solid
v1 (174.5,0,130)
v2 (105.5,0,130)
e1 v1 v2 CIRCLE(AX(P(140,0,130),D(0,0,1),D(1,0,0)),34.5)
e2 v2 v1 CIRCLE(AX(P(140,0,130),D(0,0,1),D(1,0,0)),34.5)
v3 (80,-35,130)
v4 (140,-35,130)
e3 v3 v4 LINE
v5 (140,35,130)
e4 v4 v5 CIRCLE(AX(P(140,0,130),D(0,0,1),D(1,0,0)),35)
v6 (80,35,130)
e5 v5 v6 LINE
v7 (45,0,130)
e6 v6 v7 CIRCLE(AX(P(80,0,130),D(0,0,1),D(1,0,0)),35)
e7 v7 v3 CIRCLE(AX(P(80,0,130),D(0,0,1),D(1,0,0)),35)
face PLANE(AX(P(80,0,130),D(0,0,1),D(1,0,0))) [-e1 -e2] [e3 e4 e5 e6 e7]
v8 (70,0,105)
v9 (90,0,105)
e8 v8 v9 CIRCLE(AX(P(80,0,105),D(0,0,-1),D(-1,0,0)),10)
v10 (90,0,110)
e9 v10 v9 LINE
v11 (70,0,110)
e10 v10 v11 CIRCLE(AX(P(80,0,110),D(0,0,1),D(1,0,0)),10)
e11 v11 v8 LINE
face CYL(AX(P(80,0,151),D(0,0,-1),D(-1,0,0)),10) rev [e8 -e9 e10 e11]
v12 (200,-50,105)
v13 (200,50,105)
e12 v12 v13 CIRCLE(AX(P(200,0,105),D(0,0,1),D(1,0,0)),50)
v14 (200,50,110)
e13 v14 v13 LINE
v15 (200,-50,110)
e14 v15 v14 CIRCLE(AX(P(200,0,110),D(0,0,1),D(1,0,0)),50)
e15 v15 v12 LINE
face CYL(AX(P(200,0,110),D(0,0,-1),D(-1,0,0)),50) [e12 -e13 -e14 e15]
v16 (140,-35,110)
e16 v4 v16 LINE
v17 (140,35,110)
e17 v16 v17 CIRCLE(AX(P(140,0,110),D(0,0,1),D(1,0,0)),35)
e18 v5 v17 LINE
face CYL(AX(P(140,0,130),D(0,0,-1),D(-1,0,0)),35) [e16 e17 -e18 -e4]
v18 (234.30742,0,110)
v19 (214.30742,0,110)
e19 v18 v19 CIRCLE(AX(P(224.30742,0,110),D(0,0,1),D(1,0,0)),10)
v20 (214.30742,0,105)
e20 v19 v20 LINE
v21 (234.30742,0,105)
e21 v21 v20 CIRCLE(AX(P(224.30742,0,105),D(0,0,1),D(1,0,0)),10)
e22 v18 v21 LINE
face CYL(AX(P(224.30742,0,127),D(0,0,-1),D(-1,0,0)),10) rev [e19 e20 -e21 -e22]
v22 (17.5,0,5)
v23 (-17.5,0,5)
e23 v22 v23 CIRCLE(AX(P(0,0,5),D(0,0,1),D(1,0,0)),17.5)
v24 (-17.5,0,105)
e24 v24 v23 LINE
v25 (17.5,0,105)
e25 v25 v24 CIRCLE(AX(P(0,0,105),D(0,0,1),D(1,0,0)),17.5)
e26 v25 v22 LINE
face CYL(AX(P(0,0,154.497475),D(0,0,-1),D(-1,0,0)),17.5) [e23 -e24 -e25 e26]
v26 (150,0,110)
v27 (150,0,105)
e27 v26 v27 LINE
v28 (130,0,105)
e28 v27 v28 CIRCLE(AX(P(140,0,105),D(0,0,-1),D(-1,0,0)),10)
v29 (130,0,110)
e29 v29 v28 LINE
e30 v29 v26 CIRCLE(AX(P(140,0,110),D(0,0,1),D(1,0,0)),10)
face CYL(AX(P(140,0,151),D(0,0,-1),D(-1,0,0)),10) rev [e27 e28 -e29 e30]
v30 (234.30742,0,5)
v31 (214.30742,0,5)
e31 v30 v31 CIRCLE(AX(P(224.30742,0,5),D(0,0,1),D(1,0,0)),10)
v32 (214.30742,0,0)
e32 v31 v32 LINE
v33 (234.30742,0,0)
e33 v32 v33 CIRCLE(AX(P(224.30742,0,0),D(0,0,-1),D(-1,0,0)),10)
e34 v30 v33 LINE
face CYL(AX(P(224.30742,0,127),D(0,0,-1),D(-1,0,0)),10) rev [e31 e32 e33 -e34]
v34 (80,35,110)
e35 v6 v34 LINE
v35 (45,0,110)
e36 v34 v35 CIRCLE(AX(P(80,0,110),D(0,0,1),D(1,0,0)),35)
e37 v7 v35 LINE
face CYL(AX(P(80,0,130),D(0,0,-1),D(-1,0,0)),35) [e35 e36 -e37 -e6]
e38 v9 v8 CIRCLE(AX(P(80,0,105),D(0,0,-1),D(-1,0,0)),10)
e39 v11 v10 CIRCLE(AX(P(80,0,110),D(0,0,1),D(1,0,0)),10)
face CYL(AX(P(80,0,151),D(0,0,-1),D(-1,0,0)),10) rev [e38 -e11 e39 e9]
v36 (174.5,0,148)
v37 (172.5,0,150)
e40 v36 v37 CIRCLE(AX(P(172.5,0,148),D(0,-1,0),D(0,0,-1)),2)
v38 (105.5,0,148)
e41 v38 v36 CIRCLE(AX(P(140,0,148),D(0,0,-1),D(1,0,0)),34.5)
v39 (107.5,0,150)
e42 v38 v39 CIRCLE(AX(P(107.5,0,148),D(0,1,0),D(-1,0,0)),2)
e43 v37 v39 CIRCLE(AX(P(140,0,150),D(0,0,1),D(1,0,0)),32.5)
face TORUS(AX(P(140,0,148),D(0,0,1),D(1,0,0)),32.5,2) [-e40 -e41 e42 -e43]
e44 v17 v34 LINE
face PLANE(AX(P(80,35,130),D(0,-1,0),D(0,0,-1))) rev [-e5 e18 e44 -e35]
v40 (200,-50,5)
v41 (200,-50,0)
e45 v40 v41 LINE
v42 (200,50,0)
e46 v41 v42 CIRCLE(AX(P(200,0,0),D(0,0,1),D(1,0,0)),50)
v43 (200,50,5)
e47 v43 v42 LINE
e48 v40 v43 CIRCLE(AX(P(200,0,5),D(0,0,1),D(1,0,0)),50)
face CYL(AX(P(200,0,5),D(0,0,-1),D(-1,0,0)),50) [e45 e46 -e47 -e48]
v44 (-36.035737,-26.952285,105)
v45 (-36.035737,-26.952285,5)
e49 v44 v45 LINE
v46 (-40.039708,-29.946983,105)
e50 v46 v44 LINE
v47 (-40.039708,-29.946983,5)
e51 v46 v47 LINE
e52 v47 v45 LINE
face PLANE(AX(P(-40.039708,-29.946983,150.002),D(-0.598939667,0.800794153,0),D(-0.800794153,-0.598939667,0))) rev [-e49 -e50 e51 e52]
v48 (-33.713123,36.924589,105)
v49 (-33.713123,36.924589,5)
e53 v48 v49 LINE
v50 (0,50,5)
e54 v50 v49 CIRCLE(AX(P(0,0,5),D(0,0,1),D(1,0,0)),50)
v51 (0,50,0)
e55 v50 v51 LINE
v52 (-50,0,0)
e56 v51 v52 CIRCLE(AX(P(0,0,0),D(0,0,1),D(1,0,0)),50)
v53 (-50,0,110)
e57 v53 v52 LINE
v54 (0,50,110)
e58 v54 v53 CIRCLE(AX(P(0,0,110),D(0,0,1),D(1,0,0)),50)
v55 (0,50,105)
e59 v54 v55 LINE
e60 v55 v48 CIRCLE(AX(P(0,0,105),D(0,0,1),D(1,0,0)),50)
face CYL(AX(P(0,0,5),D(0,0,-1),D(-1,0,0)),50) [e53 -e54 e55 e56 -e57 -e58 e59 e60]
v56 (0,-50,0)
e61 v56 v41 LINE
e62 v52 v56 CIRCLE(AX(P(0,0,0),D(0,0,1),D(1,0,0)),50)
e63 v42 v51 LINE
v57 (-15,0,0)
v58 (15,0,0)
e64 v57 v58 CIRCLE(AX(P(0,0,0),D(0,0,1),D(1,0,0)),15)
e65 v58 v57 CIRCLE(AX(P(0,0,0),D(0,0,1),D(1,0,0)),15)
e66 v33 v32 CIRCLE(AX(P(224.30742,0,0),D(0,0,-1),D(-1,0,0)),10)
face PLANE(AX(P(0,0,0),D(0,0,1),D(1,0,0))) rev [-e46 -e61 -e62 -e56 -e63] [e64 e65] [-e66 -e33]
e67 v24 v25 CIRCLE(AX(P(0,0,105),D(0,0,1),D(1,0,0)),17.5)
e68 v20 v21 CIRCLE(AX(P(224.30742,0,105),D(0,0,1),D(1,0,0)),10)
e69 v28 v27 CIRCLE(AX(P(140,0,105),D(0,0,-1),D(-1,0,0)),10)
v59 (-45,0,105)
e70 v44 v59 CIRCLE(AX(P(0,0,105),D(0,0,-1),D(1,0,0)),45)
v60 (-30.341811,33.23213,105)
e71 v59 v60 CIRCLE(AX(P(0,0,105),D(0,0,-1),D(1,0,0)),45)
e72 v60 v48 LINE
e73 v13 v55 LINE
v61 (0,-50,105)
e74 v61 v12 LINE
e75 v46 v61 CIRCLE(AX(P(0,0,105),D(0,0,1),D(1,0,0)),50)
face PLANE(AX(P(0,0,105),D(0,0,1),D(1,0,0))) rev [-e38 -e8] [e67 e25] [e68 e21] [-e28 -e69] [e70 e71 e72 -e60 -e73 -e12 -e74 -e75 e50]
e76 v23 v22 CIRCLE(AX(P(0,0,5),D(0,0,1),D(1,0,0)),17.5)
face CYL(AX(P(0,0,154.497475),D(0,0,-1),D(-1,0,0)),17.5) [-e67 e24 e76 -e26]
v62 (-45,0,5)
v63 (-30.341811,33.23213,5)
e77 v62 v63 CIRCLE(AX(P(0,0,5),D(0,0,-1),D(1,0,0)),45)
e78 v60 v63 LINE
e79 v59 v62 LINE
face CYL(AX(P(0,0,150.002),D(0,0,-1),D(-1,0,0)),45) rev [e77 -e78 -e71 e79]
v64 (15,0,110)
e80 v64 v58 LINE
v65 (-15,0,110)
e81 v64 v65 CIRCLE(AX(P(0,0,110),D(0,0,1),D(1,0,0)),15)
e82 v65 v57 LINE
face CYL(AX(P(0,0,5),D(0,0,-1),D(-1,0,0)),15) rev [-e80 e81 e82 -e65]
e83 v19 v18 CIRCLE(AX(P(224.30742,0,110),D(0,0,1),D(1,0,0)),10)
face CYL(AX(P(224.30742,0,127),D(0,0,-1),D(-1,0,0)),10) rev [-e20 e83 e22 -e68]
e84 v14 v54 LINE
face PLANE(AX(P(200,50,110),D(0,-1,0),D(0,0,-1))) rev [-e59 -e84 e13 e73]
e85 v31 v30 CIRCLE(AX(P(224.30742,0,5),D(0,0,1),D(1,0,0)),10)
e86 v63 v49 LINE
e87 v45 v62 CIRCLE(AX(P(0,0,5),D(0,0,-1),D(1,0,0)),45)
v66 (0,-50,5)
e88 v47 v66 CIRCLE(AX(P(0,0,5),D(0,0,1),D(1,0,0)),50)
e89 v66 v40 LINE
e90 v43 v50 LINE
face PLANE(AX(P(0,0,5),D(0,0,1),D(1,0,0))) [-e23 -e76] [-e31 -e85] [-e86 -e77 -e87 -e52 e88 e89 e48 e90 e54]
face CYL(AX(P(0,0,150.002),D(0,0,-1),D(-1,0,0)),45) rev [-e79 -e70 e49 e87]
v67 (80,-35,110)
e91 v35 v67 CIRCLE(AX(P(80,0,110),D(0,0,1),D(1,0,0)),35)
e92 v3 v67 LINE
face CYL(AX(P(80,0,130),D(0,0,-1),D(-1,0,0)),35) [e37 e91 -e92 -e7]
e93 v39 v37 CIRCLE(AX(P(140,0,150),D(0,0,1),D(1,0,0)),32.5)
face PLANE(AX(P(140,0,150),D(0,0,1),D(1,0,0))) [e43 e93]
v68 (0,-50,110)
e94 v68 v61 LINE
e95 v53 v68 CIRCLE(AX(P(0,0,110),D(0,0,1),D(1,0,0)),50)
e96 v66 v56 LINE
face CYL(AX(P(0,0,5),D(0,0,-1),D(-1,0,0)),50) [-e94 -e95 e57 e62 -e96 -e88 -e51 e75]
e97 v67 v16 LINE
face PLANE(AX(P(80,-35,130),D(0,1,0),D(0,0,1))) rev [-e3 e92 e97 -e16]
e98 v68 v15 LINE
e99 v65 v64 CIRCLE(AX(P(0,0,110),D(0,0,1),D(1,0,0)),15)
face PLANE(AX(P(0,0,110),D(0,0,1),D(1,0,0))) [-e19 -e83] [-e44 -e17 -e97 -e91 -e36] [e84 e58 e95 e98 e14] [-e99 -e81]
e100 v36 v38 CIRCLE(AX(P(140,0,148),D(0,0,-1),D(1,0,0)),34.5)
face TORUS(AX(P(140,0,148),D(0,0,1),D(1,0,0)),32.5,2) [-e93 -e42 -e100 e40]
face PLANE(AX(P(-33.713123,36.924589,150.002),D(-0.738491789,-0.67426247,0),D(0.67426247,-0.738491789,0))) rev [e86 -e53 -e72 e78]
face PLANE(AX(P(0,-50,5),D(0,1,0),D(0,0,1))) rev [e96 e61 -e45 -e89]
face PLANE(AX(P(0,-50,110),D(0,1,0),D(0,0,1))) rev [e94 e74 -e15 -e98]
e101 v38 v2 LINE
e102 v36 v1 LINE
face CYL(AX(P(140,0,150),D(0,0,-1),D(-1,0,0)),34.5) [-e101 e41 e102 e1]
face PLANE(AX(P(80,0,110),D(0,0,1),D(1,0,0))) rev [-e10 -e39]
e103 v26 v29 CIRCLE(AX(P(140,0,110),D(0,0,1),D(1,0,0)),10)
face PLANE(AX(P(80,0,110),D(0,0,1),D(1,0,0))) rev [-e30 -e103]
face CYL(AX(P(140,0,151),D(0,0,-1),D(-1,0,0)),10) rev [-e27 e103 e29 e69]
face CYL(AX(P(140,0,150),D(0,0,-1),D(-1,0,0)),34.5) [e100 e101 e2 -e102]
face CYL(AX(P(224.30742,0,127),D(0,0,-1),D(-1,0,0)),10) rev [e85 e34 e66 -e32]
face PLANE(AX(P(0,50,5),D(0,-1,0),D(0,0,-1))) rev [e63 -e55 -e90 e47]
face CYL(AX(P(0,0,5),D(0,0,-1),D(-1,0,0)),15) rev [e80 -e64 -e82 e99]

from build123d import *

# Parameters (mm, degrees)
SKETCH5_R           = 15
BOSS_EXTRUDE2_DEPTH = 5
BOSS_EXTRUDE3_START = 100
SKETCH6_R           = 15
BOSS_EXTRUDE3_DEPTH = 5
SKETCH7_R           = 17.5
SKETCH7_R_2         = 15
BOSS_EXTRUDE4_DEPTH = 100
SKETCH8_R           = 10
CUT_EXTRUDE1_DEPTH  = 46
BOSS_EXTRUDE5_DEPTH = 20
SKETCH10_R          = 34.5
BOSS_EXTRUDE6_DEPTH = 20
SKETCH11_R          = 10
CUT_EXTRUDE2_DEPTH  = 127
BOSS_EXTRUDE8_REACH = 295.3
FILLET1_R           = 2


with BuildPart() as part:
    # Sketch5 → Boss-Extrude2 (new body)
    with BuildSketch(Plane.XY):
        with BuildLine():
            Line((0, 50), (200, 50))
            ThreePointArc((200, 50), (250, 0), (200, -50))
            Line((200, -50), (0, -50))
            ThreePointArc((0, -50), (-50, 0), (0, 50))
        make_face()
        Circle(SKETCH5_R, mode=Mode.SUBTRACT)
    extrude(amount=BOSS_EXTRUDE2_DEPTH)



with BuildPart() as body_2:
    # Sketch6 → Boss-Extrude3 (new body)
    with BuildSketch(Plane.XY.offset(5).offset(BOSS_EXTRUDE3_START)):
        with BuildLine():
            Line((0, -50), (200, -50))
            ThreePointArc((200, -50), (250, 0), (200, 50))
            Line((200, 50), (0, 50))
            ThreePointArc((0, 50), (-50, 0), (0, -50))
        make_face()
        Circle(SKETCH6_R, mode=Mode.SUBTRACT)
    extrude(amount=BOSS_EXTRUDE3_DEPTH)


with BuildPart() as part_1:
    add(part.part)

    add(body_2.part)  # Boss-Extrude4 merges body 2
    # Sketch7 → Boss-Extrude4 (add)
    with BuildSketch(Plane.XY.offset(5)):
        Circle(SKETCH7_R)
        Circle(SKETCH7_R_2, mode=Mode.SUBTRACT)
    extrude(amount=BOSS_EXTRUDE4_DEPTH)

    # Sketch8 → Cut-Extrude1 (cut)
    with BuildSketch(Plane(origin=(0, 0, 105), x_dir=(-1, 0, 0), z_dir=(0, 0, -1))):
        with Locations((-80, 0)):
            Circle(SKETCH8_R)
        with Locations((-140, 0)):
            Circle(SKETCH8_R)
    extrude(amount=-CUT_EXTRUDE1_DEPTH, mode=Mode.SUBTRACT)

    # Sketch9 → Boss-Extrude5 (add)
    with BuildSketch(Plane.XY.offset(110)):
        with BuildLine():
            Line((80, 35), (140, 35))
            ThreePointArc((140, 35), (175, 0), (140, -35))
            Line((140, -35), (80, -35))
            ThreePointArc((80, -35), (45, 0), (80, 35))
        make_face()
    extrude(amount=BOSS_EXTRUDE5_DEPTH)

    # Sketch10 → Boss-Extrude6 (add)
    with BuildSketch(Plane.XY.offset(130)):
        with Locations((140, 0)):
            Circle(SKETCH10_R)
    extrude(amount=BOSS_EXTRUDE6_DEPTH)

    # Sketch11 → Cut-Extrude2 (cut)
    with BuildSketch(Plane(origin=(0, 0, 0), x_dir=(-1, 0, 0), z_dir=(0, 0, -1))):
        with Locations(Location((-224.307420274, 0, 0), (0, 0, 180))):
            Circle(SKETCH11_R)
    extrude(amount=-CUT_EXTRUDE2_DEPTH, mode=Mode.SUBTRACT)

    # Sketch13 → Boss-Extrude8 (add, up to next)
    with BuildSketch(Plane.XY.offset(5), mode=Mode.PRIVATE) as boss_extrude8_sk1:
        with BuildLine():
            Line((-33.713123493, 36.924589427), (-30.341811144, 33.232130484))
            ThreePointArc((-30.341811144, 33.232130484), (-44.79995187, 4.238432777), (-36.035736887, -26.952285005))
            Line((-36.035736887, -26.952285005), (-40.039707652, -29.946983339))
            ThreePointArc((-40.039707652, -29.946983339), (-49.777724301, 4.709369752), (-33.713123493, 36.924589427))
        make_face()
    boss_extrude8_tool1 = extrude(boss_extrude8_sk1.sketch, amount=BOSS_EXTRUDE8_REACH, mode=Mode.PRIVATE) - part_1.part
    add(boss_extrude8_tool1.solids().sort_by_distance((-32.542205, 34.608391, 5))[0])

    # Fillet1
    fillet1_edges = [part_1.edges().sort_by_distance(p)[0] for p in [
        (105.5, 0, 150),
    ]]
    fillet(fillet1_edges, radius=FILLET1_R)


solid = part_1.part
